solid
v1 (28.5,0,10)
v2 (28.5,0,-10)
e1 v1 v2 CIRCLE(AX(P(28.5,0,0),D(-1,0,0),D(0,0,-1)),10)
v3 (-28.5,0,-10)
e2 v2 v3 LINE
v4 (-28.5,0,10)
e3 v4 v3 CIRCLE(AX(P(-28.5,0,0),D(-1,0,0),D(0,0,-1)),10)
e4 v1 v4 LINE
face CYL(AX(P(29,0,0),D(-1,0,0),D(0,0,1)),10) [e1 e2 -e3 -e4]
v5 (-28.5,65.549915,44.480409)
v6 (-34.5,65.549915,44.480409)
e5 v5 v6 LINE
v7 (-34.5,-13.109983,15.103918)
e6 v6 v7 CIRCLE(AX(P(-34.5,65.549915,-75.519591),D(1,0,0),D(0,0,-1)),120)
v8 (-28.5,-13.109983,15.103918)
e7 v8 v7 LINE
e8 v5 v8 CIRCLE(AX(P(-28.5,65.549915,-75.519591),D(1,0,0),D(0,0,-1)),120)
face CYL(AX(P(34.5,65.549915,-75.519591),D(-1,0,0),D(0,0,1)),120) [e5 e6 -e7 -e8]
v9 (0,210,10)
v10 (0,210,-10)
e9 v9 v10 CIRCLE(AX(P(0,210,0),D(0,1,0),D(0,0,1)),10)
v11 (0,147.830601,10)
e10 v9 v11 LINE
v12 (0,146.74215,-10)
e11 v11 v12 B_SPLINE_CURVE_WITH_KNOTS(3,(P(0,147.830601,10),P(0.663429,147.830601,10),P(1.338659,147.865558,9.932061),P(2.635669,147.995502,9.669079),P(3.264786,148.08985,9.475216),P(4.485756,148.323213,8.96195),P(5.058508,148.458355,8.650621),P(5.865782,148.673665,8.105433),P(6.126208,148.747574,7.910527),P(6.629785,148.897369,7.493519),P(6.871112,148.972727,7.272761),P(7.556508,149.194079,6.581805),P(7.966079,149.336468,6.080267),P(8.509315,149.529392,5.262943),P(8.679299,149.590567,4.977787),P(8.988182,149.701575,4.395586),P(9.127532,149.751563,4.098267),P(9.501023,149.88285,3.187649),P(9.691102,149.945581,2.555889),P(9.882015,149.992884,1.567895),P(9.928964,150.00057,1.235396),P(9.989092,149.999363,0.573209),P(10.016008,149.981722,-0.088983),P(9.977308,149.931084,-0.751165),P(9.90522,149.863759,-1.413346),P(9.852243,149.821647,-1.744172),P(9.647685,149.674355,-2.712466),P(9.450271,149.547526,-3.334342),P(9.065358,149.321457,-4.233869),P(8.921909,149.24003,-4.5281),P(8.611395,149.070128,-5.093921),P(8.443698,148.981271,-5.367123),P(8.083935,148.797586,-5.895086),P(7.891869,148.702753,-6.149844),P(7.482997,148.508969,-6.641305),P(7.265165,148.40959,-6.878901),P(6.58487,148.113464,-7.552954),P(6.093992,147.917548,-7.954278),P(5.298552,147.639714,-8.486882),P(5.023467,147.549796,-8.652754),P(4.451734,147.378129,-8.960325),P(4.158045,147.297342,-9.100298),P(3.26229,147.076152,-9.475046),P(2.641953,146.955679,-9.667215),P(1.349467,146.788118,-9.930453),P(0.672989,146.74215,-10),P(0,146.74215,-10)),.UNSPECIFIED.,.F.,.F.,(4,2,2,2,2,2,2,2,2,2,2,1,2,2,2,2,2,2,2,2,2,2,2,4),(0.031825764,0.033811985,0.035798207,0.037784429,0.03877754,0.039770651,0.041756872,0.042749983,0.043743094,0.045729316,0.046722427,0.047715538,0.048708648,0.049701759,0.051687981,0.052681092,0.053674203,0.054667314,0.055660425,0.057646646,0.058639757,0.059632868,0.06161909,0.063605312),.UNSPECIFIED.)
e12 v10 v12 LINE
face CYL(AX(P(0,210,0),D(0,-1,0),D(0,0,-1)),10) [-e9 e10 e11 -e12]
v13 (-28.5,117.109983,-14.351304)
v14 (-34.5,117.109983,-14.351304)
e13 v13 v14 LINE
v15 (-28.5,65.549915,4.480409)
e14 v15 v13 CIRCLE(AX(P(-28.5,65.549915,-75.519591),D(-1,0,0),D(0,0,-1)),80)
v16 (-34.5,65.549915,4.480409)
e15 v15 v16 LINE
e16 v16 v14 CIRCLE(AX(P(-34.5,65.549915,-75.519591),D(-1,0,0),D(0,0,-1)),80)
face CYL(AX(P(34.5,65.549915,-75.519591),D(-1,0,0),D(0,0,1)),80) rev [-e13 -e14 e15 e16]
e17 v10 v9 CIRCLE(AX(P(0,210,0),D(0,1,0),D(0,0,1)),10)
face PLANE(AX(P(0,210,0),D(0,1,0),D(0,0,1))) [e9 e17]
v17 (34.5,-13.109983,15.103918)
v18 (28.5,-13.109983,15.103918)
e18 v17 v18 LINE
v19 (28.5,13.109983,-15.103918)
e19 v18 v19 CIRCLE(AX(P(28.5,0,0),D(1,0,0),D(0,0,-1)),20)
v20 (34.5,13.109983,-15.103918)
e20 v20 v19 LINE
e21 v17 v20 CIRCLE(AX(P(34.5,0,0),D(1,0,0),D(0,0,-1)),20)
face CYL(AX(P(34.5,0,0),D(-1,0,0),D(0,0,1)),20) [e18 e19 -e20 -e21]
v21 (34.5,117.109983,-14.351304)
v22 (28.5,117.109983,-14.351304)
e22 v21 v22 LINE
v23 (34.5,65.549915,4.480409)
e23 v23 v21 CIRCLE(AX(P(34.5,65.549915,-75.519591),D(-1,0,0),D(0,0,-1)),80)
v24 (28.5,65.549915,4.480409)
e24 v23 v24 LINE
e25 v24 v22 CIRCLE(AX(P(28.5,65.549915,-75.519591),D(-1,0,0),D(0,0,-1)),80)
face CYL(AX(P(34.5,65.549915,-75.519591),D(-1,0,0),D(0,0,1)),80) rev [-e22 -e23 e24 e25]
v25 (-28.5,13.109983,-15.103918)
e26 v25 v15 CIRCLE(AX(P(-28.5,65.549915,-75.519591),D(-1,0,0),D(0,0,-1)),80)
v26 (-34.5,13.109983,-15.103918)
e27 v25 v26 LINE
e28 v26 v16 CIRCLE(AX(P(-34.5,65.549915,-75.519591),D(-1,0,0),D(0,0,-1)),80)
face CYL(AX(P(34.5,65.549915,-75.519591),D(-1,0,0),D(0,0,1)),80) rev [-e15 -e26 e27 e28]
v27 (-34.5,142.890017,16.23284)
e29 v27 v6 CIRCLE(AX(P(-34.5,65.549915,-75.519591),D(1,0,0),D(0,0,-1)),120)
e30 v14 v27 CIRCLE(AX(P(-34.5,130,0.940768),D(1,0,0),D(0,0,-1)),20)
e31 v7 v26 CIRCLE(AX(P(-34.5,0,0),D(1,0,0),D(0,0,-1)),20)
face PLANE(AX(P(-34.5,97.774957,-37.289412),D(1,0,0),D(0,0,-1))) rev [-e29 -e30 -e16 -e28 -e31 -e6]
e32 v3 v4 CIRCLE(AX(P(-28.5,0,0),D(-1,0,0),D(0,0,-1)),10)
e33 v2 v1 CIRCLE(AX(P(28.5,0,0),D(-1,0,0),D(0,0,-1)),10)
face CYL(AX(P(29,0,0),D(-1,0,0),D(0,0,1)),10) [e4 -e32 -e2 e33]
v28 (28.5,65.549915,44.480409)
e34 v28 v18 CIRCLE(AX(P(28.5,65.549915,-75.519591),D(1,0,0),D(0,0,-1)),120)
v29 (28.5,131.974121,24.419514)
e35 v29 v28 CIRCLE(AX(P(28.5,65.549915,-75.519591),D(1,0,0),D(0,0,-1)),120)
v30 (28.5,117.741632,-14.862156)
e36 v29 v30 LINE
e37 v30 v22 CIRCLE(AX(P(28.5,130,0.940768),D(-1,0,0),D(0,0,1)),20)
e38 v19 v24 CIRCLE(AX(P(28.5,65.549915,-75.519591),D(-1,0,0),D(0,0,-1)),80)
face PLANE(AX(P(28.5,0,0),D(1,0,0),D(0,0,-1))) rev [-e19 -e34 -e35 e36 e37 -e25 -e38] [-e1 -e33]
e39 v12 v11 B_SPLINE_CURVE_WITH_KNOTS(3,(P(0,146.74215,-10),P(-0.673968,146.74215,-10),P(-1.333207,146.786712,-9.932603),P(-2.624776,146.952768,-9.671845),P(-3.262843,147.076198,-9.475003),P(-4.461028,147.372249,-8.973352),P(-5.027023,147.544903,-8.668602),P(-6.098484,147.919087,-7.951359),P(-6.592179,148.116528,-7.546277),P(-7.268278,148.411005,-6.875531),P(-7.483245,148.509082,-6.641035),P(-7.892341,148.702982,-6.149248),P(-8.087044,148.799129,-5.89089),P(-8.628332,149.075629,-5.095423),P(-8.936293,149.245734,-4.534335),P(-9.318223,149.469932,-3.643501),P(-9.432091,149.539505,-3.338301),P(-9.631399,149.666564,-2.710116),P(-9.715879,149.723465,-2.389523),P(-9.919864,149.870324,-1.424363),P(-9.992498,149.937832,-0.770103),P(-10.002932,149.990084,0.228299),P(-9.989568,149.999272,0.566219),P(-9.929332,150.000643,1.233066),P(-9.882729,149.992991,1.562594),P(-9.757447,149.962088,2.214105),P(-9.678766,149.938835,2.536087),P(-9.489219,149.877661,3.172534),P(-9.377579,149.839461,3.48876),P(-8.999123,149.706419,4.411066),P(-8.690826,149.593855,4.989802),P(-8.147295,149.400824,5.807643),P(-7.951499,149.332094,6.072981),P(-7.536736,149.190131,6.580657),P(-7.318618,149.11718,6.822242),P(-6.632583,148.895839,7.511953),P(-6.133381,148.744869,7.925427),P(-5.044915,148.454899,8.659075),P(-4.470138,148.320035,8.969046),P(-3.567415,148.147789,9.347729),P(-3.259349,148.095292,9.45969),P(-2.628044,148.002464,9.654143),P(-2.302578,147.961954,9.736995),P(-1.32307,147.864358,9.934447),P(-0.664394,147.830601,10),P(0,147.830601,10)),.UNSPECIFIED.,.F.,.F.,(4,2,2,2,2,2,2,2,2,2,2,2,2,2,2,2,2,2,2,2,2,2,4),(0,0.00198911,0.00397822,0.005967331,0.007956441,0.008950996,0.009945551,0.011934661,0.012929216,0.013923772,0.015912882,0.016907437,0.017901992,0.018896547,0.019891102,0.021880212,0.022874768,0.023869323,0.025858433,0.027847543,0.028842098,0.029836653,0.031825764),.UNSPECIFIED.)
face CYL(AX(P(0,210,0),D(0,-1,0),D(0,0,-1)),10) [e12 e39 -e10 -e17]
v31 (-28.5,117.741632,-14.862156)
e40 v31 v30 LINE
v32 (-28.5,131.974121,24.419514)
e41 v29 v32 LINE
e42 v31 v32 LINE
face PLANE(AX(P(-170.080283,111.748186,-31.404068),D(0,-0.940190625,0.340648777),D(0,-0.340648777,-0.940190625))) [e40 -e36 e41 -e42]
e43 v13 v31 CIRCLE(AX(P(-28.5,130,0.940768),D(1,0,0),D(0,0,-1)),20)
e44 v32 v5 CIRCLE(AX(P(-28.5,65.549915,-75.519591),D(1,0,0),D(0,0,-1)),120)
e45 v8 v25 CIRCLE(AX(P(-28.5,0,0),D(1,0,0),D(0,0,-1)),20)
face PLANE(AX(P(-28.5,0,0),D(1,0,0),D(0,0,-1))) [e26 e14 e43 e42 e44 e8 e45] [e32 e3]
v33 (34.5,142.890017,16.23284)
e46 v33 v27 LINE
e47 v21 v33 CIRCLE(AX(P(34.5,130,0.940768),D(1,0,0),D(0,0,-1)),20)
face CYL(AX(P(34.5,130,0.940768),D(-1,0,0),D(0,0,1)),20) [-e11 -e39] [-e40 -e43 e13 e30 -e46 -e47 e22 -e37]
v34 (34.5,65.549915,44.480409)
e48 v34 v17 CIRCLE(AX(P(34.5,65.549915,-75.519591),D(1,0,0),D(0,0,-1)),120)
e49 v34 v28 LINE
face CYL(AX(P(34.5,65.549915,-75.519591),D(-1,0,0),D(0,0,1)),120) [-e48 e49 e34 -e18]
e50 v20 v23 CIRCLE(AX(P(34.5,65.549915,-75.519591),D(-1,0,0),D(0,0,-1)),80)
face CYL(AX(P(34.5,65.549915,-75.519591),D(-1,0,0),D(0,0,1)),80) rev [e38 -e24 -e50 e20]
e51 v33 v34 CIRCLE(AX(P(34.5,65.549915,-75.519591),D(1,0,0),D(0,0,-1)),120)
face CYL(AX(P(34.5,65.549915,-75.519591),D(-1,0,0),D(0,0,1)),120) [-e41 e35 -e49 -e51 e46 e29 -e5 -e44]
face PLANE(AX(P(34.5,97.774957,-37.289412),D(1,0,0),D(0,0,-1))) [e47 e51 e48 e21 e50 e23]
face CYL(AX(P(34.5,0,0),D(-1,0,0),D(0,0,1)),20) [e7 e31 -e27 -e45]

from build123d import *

# Parameters (mm, degrees)
BOSS_EXTRUDE1_DEPTH             = 34.5
SKETCH2_R                       = 100
CUT_EXTRUDE1_DEPTH              = 28.5
CUT_EXTRUDE2_DEPTH              = 57
SKETCH5_R                       = 10
BOSS_EXTRUDE2_DEPTH             = 29
BOSS_EXTRUDE3_REACH             = 229.088
BOSS_EXTRUDE3_END_RADIUS        = 20
SKETCH7_R                       = 10
BOSS_EXTRUDE3_DIRECTION_2_DEPTH = 10


with BuildPart() as part:
    # Sketch1 → Boss-Extrude1 (new, symmetric)
    with BuildSketch(Plane(origin=(0, 0, 0), x_dir=(0, 0, -1), z_dir=(1, 0, 0))):
        with BuildLine():
            ThreePointArc((-16.232839847, 142.89001702), (-44.477266745, 64.681536406), (-15.103918242, -13.10998298))
            ThreePointArc((-15.103918242, -13.10998298), (13.10998298, -15.103918242), (15.103918242, 13.10998298))
            ThreePointArc((15.103918242, 13.10998298), (-4.478314094, 64.970995905), (14.351303838, 117.10998298))
            ThreePointArc((14.351303838, 117.10998298), (11.949249015, 145.292071843), (-16.232839847, 142.89001702))
        make_face()
    extrude(amount=BOSS_EXTRUDE1_DEPTH, both=True)

    # Sketch2 → Cut-Extrude1 (cut, symmetric)
    with BuildSketch(Plane(origin=(0, 0, 0), x_dir=(0, 0, -1), z_dir=(1, 0, 0))):
        Circle(SKETCH2_R)
    extrude(amount=CUT_EXTRUDE1_DEPTH, both=True, mode=Mode.SUBTRACT)

    # Sketch4 → Cut-Extrude2 (cut)
    with BuildSketch(Plane.ZY.offset(-28.5)):
        Polygon((-31.404068156, 111.748185713), (46.911557074, 140.123412246), (75.162269232, 67.90846072), (-19.75286352, 46.910793085), align=None)
    extrude(amount=CUT_EXTRUDE2_DEPTH, mode=Mode.SUBTRACT)

    # Sketch5 → Boss-Extrude2 (add, symmetric)
    with BuildSketch(Plane(origin=(0, 0, 0), x_dir=(0, 0, -1), z_dir=(1, 0, 0))):
        Circle(SKETCH5_R)
    extrude(amount=BOSS_EXTRUDE2_DEPTH, both=True)

    # Boss-Extrude3: up to this cylinder (the profile starts outside it)
    boss_extrude3_end = Plane(origin=(0, 130, 0.940768004), z_dir=(-1, 0, 0)) * Cylinder(BOSS_EXTRUDE3_END_RADIUS, 499.176, mode=Mode.PRIVATE)
    # Sketch7 → Boss-Extrude3 (add, up to the surface)
    with BuildSketch(Plane(origin=(0, 200, 0), x_dir=(1, 0, 0), z_dir=(0, 1, 0)), mode=Mode.PRIVATE) as boss_extrude3_sk1:
        with Locations(Location((0, 0, 0), (0, 0, 90))):
            Circle(SKETCH7_R)
    boss_extrude3_tool1 = extrude(boss_extrude3_sk1.sketch, amount=-BOSS_EXTRUDE3_REACH, mode=Mode.PRIVATE) - boss_extrude3_end
    add(boss_extrude3_tool1.solids().sort_by_distance((0, 200, 0))[0])

    # Sketch7 → Boss-Extrude3 direction 2 (add)
    with BuildSketch(Plane(origin=(0, 200, 0), x_dir=(1, 0, 0), z_dir=(0, 1, 0))):
        with Locations(Location((0, 0, 0), (0, 0, 90))):
            Circle(SKETCH7_R)
    extrude(amount=BOSS_EXTRUDE3_DIRECTION_2_DEPTH)


solid = part.part
